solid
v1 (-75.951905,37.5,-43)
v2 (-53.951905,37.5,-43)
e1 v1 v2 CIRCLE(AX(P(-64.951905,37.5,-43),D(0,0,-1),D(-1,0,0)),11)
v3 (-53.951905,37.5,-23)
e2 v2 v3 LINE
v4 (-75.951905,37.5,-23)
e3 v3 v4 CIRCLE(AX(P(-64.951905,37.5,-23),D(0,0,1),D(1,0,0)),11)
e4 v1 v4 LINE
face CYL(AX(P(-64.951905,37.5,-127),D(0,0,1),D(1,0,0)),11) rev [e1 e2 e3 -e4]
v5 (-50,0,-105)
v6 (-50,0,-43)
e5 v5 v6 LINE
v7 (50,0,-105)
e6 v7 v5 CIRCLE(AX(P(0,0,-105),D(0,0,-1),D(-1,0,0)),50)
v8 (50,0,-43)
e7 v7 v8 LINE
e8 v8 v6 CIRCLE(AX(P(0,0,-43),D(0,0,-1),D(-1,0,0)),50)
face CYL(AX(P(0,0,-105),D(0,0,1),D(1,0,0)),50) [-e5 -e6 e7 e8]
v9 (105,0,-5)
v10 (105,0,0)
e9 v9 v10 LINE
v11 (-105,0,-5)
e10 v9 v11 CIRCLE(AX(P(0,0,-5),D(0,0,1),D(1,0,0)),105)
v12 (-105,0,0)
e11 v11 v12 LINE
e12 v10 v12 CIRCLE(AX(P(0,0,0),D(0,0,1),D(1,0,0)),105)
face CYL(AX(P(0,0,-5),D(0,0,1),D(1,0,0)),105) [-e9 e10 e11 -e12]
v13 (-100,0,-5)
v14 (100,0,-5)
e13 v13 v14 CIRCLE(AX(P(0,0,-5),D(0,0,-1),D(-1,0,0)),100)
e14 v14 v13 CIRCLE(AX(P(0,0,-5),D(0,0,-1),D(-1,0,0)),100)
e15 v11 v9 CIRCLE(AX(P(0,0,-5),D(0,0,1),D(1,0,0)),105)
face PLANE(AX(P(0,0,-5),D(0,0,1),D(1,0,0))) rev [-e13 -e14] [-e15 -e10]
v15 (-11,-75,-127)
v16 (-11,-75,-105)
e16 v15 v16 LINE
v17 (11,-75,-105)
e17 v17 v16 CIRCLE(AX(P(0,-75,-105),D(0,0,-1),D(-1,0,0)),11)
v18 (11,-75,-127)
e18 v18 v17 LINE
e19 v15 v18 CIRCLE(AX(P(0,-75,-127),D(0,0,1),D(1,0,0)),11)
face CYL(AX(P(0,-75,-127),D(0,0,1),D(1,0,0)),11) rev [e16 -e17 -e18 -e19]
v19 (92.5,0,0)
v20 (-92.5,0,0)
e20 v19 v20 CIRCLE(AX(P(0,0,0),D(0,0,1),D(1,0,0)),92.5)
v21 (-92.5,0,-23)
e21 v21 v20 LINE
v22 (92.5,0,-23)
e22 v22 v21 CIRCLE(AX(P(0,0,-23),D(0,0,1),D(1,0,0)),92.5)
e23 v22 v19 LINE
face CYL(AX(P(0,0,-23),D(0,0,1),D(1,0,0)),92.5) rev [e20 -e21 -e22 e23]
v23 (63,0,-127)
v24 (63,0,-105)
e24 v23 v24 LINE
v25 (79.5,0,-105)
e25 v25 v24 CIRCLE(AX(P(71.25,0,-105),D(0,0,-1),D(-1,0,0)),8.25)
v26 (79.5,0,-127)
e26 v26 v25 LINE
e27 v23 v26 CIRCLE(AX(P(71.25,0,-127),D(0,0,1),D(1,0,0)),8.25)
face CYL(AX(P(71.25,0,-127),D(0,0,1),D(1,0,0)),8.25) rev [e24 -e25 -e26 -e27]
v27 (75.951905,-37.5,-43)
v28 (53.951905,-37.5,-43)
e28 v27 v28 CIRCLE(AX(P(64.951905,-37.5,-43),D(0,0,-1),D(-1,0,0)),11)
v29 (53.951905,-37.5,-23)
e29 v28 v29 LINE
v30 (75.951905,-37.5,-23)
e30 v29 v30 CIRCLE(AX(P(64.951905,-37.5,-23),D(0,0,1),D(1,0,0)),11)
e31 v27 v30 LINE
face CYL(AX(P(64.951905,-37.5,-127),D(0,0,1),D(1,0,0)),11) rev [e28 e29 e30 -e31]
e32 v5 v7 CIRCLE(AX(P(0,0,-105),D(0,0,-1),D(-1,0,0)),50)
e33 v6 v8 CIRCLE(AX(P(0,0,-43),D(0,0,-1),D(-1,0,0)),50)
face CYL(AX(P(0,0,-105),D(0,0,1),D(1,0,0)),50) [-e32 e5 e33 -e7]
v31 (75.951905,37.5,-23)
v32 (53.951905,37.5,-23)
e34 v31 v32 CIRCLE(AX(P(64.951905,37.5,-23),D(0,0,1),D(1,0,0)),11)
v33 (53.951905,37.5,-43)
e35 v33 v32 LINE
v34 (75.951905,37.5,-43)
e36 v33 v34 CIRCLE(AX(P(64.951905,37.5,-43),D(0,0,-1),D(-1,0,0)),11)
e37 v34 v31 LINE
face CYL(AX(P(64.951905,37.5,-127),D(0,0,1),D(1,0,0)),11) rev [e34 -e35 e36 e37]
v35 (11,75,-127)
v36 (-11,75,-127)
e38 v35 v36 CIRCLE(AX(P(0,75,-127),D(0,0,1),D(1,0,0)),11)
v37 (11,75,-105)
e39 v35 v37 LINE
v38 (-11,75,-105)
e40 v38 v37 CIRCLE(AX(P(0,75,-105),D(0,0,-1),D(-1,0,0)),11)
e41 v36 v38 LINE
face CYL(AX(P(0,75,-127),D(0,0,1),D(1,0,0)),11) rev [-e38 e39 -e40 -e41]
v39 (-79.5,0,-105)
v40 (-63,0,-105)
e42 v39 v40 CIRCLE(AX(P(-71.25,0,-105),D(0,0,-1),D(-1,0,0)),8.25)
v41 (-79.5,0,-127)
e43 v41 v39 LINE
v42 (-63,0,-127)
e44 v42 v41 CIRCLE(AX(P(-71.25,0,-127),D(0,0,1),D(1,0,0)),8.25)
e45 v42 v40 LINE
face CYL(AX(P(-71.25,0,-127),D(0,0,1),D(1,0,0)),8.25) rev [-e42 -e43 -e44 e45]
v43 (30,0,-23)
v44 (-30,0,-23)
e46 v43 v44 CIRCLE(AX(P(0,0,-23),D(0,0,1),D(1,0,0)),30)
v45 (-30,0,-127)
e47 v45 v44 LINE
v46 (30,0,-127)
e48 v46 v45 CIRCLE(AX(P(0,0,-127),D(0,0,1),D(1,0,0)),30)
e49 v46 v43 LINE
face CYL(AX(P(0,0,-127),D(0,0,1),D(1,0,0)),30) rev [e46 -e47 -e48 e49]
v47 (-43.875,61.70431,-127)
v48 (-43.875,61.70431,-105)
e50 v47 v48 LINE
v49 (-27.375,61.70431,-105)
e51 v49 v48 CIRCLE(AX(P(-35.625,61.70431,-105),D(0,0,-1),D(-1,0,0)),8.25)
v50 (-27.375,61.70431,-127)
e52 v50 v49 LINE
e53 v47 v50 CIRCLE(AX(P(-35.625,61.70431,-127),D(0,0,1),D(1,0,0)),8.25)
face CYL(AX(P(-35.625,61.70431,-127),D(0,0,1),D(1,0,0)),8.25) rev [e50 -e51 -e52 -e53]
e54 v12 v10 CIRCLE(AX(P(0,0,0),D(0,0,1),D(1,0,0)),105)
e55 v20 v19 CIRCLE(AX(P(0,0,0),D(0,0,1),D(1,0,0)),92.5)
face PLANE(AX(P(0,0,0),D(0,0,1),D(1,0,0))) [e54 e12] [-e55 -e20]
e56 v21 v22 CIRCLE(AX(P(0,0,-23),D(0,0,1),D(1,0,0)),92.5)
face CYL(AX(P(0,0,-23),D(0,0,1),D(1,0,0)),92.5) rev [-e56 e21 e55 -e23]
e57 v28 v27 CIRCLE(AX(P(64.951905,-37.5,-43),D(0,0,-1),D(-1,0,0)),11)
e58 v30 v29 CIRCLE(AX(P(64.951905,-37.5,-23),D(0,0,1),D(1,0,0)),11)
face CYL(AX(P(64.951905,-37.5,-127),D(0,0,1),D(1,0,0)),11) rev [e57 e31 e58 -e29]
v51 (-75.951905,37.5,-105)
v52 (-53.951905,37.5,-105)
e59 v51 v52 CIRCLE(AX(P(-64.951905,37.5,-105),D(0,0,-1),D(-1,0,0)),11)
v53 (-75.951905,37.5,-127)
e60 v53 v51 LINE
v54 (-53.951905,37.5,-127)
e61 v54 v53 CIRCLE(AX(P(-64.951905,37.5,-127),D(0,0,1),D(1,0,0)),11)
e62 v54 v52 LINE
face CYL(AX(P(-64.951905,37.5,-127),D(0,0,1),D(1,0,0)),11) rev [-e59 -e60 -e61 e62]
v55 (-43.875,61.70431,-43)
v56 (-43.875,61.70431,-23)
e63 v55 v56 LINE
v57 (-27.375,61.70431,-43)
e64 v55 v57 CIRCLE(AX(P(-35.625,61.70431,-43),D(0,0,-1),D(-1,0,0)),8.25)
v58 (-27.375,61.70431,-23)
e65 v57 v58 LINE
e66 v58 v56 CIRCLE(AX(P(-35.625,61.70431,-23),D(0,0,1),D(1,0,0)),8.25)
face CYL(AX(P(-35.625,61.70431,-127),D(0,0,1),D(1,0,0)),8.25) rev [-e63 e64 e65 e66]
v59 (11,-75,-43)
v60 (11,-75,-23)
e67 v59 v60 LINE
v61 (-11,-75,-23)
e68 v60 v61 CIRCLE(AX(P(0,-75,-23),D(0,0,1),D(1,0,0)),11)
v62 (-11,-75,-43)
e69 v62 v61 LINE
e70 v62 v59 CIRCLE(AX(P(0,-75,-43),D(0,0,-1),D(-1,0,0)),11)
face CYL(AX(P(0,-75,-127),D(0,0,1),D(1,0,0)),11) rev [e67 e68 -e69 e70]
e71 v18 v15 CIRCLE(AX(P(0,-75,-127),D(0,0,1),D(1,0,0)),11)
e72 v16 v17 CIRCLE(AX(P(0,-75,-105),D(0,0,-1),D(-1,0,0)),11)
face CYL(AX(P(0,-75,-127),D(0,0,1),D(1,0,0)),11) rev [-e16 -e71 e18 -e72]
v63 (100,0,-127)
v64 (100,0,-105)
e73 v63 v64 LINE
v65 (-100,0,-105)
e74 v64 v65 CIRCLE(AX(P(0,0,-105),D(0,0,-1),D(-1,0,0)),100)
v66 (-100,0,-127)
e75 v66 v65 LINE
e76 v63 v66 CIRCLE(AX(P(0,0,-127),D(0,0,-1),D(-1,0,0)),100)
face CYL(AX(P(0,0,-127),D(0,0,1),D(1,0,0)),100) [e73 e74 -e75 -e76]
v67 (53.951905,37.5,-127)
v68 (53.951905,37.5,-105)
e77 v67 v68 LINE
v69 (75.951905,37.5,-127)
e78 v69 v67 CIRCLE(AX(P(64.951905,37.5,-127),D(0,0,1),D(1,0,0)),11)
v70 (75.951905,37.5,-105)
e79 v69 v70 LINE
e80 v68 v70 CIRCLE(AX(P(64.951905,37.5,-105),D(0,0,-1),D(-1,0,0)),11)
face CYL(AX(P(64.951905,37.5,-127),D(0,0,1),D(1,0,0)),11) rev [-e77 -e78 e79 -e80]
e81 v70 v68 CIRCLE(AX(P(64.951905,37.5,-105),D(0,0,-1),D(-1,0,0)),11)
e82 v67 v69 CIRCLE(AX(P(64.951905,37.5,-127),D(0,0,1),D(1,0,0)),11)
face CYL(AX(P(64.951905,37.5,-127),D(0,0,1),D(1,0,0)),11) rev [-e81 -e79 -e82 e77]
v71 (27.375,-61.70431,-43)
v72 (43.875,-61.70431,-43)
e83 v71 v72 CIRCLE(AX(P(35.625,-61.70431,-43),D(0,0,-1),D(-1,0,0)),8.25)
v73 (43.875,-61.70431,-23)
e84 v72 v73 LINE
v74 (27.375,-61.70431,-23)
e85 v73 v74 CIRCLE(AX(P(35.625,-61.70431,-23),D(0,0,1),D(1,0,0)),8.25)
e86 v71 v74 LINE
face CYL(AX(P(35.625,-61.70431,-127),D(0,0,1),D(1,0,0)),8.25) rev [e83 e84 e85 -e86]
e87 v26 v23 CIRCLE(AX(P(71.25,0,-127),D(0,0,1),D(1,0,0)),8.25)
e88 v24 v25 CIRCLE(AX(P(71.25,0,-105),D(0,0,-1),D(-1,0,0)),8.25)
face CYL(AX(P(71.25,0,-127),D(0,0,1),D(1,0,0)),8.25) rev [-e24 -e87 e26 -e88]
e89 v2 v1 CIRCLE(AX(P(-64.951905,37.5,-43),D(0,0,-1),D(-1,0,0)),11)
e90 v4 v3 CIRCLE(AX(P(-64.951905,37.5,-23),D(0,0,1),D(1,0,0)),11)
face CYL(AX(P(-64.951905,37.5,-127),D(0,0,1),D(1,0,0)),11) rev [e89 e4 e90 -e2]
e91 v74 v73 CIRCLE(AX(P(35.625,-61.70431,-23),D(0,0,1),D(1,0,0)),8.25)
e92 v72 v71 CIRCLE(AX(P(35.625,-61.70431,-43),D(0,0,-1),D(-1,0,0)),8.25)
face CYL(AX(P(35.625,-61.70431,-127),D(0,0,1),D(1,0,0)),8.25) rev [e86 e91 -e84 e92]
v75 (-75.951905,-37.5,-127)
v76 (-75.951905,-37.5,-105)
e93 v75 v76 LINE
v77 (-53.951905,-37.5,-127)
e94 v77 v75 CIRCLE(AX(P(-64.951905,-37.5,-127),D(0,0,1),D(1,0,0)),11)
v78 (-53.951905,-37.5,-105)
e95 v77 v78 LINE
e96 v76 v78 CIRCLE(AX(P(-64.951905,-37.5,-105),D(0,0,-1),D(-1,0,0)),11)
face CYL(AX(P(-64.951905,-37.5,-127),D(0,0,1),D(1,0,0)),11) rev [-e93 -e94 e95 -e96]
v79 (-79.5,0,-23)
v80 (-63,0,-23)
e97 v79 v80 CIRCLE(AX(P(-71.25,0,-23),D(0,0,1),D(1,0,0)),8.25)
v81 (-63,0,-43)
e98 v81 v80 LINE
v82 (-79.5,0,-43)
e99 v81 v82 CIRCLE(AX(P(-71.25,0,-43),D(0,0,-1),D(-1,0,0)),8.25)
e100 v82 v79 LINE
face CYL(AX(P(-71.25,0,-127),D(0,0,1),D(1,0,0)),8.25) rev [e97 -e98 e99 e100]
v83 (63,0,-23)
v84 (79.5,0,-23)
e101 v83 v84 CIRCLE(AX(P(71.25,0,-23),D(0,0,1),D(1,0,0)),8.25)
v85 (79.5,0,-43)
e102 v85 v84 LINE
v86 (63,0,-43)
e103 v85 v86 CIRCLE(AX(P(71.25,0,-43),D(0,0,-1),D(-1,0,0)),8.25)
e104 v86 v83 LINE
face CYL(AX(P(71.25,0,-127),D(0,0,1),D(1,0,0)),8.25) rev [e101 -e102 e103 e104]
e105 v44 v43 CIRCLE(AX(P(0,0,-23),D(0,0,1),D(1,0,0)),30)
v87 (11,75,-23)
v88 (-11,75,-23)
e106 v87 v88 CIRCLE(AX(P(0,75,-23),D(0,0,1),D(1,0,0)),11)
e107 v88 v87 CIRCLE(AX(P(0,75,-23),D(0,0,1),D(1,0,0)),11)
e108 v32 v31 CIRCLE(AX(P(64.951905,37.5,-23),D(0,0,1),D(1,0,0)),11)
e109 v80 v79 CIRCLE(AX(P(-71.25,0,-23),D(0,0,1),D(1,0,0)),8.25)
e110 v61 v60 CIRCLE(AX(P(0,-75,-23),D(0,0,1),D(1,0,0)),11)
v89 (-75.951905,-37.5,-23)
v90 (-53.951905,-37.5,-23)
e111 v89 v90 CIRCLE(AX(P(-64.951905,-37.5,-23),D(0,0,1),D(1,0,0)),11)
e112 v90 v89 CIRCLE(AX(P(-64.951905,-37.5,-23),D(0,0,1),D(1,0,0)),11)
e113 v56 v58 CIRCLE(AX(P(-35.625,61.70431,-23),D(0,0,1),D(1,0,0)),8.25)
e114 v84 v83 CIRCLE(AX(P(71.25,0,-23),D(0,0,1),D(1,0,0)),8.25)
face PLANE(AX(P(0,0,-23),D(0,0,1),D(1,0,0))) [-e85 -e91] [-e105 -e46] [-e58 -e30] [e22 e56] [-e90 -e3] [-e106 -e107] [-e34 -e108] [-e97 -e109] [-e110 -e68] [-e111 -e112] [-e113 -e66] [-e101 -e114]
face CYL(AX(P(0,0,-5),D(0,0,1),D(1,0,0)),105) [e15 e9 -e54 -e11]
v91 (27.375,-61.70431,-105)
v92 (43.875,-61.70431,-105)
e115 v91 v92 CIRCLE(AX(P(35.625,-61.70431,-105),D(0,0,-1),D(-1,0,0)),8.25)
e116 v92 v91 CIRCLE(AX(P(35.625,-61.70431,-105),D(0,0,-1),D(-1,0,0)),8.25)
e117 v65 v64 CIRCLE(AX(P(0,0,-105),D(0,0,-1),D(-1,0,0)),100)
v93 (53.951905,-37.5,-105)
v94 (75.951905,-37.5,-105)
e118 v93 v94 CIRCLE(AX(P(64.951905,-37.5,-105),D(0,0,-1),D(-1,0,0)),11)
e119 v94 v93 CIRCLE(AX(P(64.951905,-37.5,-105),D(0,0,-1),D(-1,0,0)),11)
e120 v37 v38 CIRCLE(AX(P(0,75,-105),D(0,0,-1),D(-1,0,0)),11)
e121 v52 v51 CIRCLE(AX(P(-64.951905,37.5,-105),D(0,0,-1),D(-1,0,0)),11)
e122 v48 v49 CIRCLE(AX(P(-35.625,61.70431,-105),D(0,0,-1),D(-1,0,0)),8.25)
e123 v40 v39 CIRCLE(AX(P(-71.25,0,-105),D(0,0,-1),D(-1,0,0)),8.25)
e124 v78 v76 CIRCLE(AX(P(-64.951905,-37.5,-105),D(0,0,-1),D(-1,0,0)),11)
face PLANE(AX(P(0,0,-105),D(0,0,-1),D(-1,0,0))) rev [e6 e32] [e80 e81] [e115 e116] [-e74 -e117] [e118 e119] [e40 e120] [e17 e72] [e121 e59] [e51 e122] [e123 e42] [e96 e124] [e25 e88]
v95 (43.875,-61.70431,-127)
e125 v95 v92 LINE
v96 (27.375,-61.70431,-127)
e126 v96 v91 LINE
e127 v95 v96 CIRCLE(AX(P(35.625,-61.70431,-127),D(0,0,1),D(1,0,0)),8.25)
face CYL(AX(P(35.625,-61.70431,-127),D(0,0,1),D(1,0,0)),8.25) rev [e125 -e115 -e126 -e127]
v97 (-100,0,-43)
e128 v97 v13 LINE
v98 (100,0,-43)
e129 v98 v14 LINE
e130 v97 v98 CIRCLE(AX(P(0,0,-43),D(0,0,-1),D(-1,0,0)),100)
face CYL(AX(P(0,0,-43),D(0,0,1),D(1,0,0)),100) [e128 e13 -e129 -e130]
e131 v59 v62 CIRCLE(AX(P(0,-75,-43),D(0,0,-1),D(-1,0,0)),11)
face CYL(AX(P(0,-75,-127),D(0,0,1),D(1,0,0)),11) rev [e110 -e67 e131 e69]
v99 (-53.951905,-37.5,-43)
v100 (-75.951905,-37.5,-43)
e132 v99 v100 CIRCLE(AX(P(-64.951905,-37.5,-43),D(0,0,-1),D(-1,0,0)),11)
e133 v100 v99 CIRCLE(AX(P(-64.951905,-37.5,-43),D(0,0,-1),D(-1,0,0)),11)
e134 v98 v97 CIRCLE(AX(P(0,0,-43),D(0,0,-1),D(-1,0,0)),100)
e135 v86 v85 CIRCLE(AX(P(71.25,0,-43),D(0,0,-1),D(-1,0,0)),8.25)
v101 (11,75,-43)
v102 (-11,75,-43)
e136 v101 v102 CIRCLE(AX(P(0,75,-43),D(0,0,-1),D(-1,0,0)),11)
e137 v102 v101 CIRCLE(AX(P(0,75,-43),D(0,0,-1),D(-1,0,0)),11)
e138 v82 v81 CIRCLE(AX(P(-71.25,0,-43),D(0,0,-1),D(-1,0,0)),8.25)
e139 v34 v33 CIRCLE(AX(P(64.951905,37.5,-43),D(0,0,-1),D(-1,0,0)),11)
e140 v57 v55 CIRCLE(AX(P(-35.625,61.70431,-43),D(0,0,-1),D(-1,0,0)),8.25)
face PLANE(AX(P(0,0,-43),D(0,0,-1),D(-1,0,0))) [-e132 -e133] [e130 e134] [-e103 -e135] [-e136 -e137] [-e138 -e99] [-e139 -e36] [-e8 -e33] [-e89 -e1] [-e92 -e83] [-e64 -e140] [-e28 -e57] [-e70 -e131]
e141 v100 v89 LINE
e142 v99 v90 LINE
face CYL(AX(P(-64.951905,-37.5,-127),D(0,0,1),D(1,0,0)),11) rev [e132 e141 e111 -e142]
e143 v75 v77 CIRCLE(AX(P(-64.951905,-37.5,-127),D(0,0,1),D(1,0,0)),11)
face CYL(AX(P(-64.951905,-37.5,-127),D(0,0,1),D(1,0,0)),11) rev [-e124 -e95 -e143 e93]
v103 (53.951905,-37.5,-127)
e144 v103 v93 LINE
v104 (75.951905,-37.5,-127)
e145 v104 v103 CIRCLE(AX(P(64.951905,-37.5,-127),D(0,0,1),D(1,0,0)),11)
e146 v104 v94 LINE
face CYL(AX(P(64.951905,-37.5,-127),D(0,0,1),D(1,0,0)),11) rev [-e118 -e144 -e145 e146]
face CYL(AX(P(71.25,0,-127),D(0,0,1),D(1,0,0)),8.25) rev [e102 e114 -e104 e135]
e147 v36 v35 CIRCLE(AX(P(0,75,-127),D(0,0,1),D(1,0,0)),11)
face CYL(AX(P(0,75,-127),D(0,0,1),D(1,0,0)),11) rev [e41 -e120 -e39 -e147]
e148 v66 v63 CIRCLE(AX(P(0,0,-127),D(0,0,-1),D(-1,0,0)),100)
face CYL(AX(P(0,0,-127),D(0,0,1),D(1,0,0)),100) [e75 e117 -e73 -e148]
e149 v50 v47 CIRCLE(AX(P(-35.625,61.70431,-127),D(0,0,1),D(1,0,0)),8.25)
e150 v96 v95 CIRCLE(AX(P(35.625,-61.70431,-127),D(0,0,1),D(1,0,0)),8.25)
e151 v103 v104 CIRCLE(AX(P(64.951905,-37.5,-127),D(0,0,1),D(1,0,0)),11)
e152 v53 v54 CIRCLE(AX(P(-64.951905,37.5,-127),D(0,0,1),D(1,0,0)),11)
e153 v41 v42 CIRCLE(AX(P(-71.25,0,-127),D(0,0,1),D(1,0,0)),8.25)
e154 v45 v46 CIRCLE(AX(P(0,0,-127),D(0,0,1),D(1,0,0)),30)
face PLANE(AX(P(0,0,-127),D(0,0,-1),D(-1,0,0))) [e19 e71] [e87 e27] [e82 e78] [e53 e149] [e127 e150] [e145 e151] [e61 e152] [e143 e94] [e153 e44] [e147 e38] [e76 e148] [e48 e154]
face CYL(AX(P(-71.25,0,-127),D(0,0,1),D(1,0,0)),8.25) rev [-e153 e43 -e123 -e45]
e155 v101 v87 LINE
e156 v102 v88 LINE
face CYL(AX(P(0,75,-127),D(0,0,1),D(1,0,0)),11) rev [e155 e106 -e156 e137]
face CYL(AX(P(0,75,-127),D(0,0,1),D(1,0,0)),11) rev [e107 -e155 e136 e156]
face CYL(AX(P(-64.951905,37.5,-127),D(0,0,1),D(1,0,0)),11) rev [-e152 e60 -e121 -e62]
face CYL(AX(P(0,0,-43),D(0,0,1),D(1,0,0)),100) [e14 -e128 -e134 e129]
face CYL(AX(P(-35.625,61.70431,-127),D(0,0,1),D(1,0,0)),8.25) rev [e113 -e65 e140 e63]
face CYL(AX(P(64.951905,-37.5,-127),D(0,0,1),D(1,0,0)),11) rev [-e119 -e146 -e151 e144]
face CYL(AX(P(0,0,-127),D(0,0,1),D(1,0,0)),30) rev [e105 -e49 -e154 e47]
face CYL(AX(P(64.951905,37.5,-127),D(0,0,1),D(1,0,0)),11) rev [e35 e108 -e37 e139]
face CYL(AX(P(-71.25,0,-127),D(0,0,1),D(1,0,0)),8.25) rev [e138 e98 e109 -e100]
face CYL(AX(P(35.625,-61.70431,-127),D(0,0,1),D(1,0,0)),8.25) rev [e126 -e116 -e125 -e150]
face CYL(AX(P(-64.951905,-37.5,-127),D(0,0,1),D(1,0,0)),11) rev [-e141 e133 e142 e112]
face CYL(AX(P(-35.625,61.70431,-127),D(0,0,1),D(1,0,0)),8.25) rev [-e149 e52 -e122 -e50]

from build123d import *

# Parameters (mm, degrees)
RIM_LIP_SKETCH_210_R      = 105
RIM_LIP_210_DEPTH         = 5
FRONT_FLANGE_SKETCH_200_R = 100
FRONT_FLANGE_200_DEPTH    = 38
HUB_BARREL_SKETCH_100_R   = 50
HUB_BARREL_100_DEPTH      = 62
REAR_FLANGE_SKETCH_200_R  = 100
REAR_FLANGE_200_DEPTH     = 22
FRONT_RECESS_SKETCH_185_R = 92.5
FRONT_RECESS_185_DEPTH    = 23
BORE_SKETCH_60_R          = 30
BORE_60_DEPTH             = 182.289823211
FLANGE_HOLES_SKETCH_R     = 11
FLANGE_HOLES_SKETCH_R_2   = 8.25
FLANGE_HOLES_DEPTH        = 182.289823211


with BuildPart() as part:
    # Rim Lip Sketch Ø210 → Rim Lip Ø210 (new body)
    with BuildSketch(Plane.XY):
        Circle(RIM_LIP_SKETCH_210_R)
    extrude(amount=-RIM_LIP_210_DEPTH)

    # Front Flange Sketch Ø200 → Front Flange Ø200 (add)
    with BuildSketch(Plane(origin=(0, 0, -5), x_dir=(-1, 0, 0), z_dir=(0, 0, -1))):
        Circle(FRONT_FLANGE_SKETCH_200_R)
    extrude(amount=FRONT_FLANGE_200_DEPTH)

    # Hub Barrel Sketch Ø100 → Hub Barrel Ø100 (add)
    with BuildSketch(Plane(origin=(0, 0, -43), x_dir=(-1, 0, 0), z_dir=(0, 0, -1))):
        Circle(HUB_BARREL_SKETCH_100_R)
    extrude(amount=HUB_BARREL_100_DEPTH)

    # Rear Flange Sketch Ø200 → Rear Flange Ø200 (add)
    with BuildSketch(Plane(origin=(0, 0, -105), x_dir=(-1, 0, 0), z_dir=(0, 0, -1))):
        Circle(REAR_FLANGE_SKETCH_200_R)
    extrude(amount=REAR_FLANGE_200_DEPTH)

    # Front Recess Sketch Ø185 → Front Recess Ø185 (cut)
    with BuildSketch(Plane.XY):
        Circle(FRONT_RECESS_SKETCH_185_R)
    extrude(amount=-FRONT_RECESS_185_DEPTH, mode=Mode.SUBTRACT)

    # Bore Sketch Ø60 → Bore Ø60 (cut, through all)
    with BuildSketch(Plane.XY.offset(-23)):
        Circle(BORE_SKETCH_60_R)
    extrude(amount=-BORE_60_DEPTH, mode=Mode.SUBTRACT)

    # Flange Holes Sketch → Flange Holes (cut, through all)
    with BuildSketch(Plane.XY.offset(-23)):
        with Locations((0, 75)):
            Circle(FLANGE_HOLES_SKETCH_R)
        with Locations((64.951905284, 37.5)):
            Circle(FLANGE_HOLES_SKETCH_R)
        with Locations((64.951905284, -37.5)):
            Circle(FLANGE_HOLES_SKETCH_R)
        with Locations((0, -75)):
            Circle(FLANGE_HOLES_SKETCH_R)
        with Locations((-64.951905284, -37.5)):
            Circle(FLANGE_HOLES_SKETCH_R)
        with Locations((-64.951905284, 37.5)):
            Circle(FLANGE_HOLES_SKETCH_R)
        with Locations((-71.25, 0)):
            Circle(FLANGE_HOLES_SKETCH_R_2)
        with Locations((71.25, 0)):
            Circle(FLANGE_HOLES_SKETCH_R_2)
        with Locations((35.625, -61.70431002)):
            Circle(FLANGE_HOLES_SKETCH_R_2)
        with Locations((-35.625, 61.70431002)):
            Circle(FLANGE_HOLES_SKETCH_R_2)
    extrude(amount=-FLANGE_HOLES_DEPTH, mode=Mode.SUBTRACT)


solid = part.part
